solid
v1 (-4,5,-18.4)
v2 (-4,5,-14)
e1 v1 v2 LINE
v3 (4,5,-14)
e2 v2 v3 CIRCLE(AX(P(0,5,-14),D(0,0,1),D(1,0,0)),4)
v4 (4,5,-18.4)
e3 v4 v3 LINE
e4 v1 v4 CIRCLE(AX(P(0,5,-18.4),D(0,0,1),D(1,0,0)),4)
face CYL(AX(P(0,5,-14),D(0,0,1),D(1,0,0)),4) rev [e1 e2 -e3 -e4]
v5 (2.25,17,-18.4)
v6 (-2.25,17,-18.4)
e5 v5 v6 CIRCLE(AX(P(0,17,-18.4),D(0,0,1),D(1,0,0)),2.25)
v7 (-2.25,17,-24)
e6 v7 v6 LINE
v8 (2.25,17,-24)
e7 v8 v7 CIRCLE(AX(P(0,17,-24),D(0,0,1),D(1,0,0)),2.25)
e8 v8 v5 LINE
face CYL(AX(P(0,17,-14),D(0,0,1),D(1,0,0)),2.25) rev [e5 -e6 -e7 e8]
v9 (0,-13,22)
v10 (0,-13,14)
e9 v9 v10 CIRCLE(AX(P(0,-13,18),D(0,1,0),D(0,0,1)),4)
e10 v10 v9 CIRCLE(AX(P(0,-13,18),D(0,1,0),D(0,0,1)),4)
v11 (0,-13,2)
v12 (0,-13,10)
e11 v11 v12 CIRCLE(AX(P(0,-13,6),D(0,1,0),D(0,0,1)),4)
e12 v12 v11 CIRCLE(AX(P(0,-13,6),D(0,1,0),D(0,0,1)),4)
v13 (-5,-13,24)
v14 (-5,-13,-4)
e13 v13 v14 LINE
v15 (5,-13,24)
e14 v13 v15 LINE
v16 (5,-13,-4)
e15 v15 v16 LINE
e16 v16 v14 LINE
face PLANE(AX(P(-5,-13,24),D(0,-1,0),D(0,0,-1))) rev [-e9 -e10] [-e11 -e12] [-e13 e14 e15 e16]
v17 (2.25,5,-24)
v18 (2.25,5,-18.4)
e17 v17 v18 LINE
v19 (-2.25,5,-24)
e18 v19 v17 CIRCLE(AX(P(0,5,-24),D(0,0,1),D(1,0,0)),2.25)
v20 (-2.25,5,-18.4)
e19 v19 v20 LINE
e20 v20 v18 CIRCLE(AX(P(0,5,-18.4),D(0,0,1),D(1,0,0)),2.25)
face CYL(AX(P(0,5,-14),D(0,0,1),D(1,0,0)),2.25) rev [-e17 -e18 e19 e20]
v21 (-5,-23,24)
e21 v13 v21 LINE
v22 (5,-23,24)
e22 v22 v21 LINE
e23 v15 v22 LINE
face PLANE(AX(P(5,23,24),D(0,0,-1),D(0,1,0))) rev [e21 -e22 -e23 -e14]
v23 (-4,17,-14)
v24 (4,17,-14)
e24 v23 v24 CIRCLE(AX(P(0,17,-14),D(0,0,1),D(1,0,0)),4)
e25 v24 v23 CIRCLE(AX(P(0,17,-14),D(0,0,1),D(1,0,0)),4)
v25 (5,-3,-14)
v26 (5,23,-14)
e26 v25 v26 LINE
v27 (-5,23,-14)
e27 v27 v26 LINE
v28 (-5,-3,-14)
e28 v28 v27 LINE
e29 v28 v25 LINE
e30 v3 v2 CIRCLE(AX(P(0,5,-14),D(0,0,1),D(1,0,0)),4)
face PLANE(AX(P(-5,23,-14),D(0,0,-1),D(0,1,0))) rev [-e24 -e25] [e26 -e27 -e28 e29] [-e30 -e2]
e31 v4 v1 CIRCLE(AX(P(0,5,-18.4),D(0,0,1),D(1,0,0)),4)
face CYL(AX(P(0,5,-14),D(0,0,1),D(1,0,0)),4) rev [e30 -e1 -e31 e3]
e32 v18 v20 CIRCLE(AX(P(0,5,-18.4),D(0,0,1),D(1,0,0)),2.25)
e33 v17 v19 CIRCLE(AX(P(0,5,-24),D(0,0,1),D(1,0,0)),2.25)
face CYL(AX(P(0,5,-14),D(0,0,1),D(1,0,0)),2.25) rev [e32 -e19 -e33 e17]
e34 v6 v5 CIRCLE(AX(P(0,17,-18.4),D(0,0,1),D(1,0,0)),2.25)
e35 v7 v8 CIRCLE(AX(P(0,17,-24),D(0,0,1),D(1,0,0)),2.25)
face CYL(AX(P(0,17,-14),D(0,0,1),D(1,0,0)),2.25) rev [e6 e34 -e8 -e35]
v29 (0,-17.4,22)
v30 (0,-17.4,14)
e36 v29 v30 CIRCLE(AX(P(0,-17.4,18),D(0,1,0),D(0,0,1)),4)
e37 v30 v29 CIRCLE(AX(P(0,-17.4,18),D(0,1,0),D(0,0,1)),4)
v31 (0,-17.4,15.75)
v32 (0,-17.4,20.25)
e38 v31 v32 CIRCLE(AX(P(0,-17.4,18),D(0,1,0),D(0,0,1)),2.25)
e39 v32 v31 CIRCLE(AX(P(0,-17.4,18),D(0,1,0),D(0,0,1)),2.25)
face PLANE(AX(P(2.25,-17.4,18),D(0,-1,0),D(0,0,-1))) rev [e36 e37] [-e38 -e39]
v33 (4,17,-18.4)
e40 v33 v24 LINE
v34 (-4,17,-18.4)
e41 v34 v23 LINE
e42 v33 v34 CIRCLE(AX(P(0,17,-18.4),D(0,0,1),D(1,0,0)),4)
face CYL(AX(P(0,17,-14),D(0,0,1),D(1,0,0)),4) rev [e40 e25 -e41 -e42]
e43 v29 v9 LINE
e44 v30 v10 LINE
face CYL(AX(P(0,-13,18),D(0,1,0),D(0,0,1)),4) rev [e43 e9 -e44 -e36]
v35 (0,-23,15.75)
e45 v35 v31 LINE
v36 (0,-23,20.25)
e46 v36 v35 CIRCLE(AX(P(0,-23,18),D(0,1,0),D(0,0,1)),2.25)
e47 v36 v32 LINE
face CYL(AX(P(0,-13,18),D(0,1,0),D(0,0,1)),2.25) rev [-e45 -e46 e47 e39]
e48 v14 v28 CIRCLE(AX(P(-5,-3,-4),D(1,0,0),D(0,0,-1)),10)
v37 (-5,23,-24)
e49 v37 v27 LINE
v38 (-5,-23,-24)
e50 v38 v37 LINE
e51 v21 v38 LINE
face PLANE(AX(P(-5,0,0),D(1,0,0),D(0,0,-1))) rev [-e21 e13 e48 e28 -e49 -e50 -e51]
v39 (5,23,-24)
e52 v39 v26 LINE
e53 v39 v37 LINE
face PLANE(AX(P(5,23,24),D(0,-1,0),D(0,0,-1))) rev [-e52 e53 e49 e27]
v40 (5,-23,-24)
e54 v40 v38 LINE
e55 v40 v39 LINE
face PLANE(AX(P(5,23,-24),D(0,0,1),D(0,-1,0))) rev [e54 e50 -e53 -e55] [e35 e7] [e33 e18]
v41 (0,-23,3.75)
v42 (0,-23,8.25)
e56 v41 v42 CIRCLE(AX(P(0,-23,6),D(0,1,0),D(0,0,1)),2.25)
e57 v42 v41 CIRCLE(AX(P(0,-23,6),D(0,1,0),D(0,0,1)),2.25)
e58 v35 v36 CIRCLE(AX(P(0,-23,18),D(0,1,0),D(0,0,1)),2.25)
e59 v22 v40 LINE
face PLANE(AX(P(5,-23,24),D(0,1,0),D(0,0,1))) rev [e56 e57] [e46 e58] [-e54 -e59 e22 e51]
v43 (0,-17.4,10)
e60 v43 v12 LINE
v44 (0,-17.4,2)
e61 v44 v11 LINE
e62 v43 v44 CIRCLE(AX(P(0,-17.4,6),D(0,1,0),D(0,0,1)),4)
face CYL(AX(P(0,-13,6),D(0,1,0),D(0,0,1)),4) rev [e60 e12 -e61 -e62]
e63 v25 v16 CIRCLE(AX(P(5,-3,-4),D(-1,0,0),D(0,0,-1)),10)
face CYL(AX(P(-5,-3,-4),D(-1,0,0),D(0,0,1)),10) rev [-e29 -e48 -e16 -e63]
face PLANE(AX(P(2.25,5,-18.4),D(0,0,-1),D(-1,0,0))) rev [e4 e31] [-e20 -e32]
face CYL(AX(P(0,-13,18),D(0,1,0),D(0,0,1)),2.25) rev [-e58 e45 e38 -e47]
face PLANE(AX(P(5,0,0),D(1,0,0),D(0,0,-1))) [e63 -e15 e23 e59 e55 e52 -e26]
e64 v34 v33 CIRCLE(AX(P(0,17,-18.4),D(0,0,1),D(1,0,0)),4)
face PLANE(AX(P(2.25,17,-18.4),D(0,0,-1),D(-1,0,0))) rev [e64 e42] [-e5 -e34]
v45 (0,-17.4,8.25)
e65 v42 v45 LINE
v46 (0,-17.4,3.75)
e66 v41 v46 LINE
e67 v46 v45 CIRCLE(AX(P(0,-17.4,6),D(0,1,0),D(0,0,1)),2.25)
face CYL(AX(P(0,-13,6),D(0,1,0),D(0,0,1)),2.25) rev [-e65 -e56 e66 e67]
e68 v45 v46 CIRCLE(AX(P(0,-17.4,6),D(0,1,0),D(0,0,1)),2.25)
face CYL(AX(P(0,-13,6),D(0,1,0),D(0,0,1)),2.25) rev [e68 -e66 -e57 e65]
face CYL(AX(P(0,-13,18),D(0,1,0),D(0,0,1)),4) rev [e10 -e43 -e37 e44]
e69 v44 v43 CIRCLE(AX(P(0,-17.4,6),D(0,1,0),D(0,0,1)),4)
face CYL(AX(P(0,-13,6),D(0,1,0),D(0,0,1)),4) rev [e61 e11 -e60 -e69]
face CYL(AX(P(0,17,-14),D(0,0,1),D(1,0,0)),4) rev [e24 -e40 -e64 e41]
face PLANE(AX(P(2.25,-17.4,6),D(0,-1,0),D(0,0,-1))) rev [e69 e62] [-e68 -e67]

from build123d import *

# Parameters (mm, degrees)
SKETCH1_W                                           = 48
SKETCH1_H                                           = 46
BOSS_EXTRUDE1_DEPTH                                 = 5
SKETCH2_W                                           = 38
SKETCH2_H                                           = 36
CUT_EXTRUDE1_DEPTH                                  = 35.713109915
FILLET1_R                                           = 10
CBORE_FOR_M4_HEX_SOCKET_HEAD_CAP_SCREW1_D           = 4.5
CBORE_FOR_M4_HEX_SOCKET_HEAD_CAP_SCREW1_CBORE_D     = 8
CBORE_FOR_M4_HEX_SOCKET_HEAD_CAP_SCREW1_CBORE_DEPTH = 4.4
CBORE_FOR_M4_HEX_SOCKET_HEAD_CAP_SCREW2_D           = 4.5
CBORE_FOR_M4_HEX_SOCKET_HEAD_CAP_SCREW2_CBORE_D     = 8
CBORE_FOR_M4_HEX_SOCKET_HEAD_CAP_SCREW2_CBORE_DEPTH = 4.4


with BuildPart() as part:
    # Sketch1 → Boss-Extrude1 (new, symmetric)
    with BuildSketch(Plane(origin=(0, 0, 0), x_dir=(0, 0, -1), z_dir=(1, 0, 0))):
        Rectangle(SKETCH1_W, SKETCH1_H)
    extrude(amount=BOSS_EXTRUDE1_DEPTH, both=True)

    # Sketch2 → Cut-Extrude1 (cut, through all)
    with BuildSketch(Plane(origin=(5, 0, 0), x_dir=(0, 0, -1), z_dir=(1, 0, 0))):
        with Locations((-5, 5)):
            Rectangle(SKETCH2_W, SKETCH2_H)
    extrude(amount=-CUT_EXTRUDE1_DEPTH, mode=Mode.SUBTRACT)

    # Fillet1
    fillet1_edges = [part.edges().sort_by_distance(p)[0] for p in [
        (0, -13, -14),
    ]]
    fillet(fillet1_edges, radius=FILLET1_R)

    # CBORE for M4 Hex Socket Head Cap Screw1 (through all)
    with Locations(Plane(origin=(0, -13, 0), x_dir=(1, 0, 0), z_dir=(0, 1, 0))):
        with Locations((0, -18), (0, -6)):
            CounterBoreHole(CBORE_FOR_M4_HEX_SOCKET_HEAD_CAP_SCREW1_D / 2, CBORE_FOR_M4_HEX_SOCKET_HEAD_CAP_SCREW1_CBORE_D / 2, CBORE_FOR_M4_HEX_SOCKET_HEAD_CAP_SCREW1_CBORE_DEPTH)

    # CBORE for M4 Hex Socket Head Cap Screw2 (through all)
    with Locations(Plane.XY.offset(-14)):
        with Locations((0, 17), (0, 5)):
            CounterBoreHole(CBORE_FOR_M4_HEX_SOCKET_HEAD_CAP_SCREW2_D / 2, CBORE_FOR_M4_HEX_SOCKET_HEAD_CAP_SCREW2_CBORE_D / 2, CBORE_FOR_M4_HEX_SOCKET_HEAD_CAP_SCREW2_CBORE_DEPTH)


solid = part.part
